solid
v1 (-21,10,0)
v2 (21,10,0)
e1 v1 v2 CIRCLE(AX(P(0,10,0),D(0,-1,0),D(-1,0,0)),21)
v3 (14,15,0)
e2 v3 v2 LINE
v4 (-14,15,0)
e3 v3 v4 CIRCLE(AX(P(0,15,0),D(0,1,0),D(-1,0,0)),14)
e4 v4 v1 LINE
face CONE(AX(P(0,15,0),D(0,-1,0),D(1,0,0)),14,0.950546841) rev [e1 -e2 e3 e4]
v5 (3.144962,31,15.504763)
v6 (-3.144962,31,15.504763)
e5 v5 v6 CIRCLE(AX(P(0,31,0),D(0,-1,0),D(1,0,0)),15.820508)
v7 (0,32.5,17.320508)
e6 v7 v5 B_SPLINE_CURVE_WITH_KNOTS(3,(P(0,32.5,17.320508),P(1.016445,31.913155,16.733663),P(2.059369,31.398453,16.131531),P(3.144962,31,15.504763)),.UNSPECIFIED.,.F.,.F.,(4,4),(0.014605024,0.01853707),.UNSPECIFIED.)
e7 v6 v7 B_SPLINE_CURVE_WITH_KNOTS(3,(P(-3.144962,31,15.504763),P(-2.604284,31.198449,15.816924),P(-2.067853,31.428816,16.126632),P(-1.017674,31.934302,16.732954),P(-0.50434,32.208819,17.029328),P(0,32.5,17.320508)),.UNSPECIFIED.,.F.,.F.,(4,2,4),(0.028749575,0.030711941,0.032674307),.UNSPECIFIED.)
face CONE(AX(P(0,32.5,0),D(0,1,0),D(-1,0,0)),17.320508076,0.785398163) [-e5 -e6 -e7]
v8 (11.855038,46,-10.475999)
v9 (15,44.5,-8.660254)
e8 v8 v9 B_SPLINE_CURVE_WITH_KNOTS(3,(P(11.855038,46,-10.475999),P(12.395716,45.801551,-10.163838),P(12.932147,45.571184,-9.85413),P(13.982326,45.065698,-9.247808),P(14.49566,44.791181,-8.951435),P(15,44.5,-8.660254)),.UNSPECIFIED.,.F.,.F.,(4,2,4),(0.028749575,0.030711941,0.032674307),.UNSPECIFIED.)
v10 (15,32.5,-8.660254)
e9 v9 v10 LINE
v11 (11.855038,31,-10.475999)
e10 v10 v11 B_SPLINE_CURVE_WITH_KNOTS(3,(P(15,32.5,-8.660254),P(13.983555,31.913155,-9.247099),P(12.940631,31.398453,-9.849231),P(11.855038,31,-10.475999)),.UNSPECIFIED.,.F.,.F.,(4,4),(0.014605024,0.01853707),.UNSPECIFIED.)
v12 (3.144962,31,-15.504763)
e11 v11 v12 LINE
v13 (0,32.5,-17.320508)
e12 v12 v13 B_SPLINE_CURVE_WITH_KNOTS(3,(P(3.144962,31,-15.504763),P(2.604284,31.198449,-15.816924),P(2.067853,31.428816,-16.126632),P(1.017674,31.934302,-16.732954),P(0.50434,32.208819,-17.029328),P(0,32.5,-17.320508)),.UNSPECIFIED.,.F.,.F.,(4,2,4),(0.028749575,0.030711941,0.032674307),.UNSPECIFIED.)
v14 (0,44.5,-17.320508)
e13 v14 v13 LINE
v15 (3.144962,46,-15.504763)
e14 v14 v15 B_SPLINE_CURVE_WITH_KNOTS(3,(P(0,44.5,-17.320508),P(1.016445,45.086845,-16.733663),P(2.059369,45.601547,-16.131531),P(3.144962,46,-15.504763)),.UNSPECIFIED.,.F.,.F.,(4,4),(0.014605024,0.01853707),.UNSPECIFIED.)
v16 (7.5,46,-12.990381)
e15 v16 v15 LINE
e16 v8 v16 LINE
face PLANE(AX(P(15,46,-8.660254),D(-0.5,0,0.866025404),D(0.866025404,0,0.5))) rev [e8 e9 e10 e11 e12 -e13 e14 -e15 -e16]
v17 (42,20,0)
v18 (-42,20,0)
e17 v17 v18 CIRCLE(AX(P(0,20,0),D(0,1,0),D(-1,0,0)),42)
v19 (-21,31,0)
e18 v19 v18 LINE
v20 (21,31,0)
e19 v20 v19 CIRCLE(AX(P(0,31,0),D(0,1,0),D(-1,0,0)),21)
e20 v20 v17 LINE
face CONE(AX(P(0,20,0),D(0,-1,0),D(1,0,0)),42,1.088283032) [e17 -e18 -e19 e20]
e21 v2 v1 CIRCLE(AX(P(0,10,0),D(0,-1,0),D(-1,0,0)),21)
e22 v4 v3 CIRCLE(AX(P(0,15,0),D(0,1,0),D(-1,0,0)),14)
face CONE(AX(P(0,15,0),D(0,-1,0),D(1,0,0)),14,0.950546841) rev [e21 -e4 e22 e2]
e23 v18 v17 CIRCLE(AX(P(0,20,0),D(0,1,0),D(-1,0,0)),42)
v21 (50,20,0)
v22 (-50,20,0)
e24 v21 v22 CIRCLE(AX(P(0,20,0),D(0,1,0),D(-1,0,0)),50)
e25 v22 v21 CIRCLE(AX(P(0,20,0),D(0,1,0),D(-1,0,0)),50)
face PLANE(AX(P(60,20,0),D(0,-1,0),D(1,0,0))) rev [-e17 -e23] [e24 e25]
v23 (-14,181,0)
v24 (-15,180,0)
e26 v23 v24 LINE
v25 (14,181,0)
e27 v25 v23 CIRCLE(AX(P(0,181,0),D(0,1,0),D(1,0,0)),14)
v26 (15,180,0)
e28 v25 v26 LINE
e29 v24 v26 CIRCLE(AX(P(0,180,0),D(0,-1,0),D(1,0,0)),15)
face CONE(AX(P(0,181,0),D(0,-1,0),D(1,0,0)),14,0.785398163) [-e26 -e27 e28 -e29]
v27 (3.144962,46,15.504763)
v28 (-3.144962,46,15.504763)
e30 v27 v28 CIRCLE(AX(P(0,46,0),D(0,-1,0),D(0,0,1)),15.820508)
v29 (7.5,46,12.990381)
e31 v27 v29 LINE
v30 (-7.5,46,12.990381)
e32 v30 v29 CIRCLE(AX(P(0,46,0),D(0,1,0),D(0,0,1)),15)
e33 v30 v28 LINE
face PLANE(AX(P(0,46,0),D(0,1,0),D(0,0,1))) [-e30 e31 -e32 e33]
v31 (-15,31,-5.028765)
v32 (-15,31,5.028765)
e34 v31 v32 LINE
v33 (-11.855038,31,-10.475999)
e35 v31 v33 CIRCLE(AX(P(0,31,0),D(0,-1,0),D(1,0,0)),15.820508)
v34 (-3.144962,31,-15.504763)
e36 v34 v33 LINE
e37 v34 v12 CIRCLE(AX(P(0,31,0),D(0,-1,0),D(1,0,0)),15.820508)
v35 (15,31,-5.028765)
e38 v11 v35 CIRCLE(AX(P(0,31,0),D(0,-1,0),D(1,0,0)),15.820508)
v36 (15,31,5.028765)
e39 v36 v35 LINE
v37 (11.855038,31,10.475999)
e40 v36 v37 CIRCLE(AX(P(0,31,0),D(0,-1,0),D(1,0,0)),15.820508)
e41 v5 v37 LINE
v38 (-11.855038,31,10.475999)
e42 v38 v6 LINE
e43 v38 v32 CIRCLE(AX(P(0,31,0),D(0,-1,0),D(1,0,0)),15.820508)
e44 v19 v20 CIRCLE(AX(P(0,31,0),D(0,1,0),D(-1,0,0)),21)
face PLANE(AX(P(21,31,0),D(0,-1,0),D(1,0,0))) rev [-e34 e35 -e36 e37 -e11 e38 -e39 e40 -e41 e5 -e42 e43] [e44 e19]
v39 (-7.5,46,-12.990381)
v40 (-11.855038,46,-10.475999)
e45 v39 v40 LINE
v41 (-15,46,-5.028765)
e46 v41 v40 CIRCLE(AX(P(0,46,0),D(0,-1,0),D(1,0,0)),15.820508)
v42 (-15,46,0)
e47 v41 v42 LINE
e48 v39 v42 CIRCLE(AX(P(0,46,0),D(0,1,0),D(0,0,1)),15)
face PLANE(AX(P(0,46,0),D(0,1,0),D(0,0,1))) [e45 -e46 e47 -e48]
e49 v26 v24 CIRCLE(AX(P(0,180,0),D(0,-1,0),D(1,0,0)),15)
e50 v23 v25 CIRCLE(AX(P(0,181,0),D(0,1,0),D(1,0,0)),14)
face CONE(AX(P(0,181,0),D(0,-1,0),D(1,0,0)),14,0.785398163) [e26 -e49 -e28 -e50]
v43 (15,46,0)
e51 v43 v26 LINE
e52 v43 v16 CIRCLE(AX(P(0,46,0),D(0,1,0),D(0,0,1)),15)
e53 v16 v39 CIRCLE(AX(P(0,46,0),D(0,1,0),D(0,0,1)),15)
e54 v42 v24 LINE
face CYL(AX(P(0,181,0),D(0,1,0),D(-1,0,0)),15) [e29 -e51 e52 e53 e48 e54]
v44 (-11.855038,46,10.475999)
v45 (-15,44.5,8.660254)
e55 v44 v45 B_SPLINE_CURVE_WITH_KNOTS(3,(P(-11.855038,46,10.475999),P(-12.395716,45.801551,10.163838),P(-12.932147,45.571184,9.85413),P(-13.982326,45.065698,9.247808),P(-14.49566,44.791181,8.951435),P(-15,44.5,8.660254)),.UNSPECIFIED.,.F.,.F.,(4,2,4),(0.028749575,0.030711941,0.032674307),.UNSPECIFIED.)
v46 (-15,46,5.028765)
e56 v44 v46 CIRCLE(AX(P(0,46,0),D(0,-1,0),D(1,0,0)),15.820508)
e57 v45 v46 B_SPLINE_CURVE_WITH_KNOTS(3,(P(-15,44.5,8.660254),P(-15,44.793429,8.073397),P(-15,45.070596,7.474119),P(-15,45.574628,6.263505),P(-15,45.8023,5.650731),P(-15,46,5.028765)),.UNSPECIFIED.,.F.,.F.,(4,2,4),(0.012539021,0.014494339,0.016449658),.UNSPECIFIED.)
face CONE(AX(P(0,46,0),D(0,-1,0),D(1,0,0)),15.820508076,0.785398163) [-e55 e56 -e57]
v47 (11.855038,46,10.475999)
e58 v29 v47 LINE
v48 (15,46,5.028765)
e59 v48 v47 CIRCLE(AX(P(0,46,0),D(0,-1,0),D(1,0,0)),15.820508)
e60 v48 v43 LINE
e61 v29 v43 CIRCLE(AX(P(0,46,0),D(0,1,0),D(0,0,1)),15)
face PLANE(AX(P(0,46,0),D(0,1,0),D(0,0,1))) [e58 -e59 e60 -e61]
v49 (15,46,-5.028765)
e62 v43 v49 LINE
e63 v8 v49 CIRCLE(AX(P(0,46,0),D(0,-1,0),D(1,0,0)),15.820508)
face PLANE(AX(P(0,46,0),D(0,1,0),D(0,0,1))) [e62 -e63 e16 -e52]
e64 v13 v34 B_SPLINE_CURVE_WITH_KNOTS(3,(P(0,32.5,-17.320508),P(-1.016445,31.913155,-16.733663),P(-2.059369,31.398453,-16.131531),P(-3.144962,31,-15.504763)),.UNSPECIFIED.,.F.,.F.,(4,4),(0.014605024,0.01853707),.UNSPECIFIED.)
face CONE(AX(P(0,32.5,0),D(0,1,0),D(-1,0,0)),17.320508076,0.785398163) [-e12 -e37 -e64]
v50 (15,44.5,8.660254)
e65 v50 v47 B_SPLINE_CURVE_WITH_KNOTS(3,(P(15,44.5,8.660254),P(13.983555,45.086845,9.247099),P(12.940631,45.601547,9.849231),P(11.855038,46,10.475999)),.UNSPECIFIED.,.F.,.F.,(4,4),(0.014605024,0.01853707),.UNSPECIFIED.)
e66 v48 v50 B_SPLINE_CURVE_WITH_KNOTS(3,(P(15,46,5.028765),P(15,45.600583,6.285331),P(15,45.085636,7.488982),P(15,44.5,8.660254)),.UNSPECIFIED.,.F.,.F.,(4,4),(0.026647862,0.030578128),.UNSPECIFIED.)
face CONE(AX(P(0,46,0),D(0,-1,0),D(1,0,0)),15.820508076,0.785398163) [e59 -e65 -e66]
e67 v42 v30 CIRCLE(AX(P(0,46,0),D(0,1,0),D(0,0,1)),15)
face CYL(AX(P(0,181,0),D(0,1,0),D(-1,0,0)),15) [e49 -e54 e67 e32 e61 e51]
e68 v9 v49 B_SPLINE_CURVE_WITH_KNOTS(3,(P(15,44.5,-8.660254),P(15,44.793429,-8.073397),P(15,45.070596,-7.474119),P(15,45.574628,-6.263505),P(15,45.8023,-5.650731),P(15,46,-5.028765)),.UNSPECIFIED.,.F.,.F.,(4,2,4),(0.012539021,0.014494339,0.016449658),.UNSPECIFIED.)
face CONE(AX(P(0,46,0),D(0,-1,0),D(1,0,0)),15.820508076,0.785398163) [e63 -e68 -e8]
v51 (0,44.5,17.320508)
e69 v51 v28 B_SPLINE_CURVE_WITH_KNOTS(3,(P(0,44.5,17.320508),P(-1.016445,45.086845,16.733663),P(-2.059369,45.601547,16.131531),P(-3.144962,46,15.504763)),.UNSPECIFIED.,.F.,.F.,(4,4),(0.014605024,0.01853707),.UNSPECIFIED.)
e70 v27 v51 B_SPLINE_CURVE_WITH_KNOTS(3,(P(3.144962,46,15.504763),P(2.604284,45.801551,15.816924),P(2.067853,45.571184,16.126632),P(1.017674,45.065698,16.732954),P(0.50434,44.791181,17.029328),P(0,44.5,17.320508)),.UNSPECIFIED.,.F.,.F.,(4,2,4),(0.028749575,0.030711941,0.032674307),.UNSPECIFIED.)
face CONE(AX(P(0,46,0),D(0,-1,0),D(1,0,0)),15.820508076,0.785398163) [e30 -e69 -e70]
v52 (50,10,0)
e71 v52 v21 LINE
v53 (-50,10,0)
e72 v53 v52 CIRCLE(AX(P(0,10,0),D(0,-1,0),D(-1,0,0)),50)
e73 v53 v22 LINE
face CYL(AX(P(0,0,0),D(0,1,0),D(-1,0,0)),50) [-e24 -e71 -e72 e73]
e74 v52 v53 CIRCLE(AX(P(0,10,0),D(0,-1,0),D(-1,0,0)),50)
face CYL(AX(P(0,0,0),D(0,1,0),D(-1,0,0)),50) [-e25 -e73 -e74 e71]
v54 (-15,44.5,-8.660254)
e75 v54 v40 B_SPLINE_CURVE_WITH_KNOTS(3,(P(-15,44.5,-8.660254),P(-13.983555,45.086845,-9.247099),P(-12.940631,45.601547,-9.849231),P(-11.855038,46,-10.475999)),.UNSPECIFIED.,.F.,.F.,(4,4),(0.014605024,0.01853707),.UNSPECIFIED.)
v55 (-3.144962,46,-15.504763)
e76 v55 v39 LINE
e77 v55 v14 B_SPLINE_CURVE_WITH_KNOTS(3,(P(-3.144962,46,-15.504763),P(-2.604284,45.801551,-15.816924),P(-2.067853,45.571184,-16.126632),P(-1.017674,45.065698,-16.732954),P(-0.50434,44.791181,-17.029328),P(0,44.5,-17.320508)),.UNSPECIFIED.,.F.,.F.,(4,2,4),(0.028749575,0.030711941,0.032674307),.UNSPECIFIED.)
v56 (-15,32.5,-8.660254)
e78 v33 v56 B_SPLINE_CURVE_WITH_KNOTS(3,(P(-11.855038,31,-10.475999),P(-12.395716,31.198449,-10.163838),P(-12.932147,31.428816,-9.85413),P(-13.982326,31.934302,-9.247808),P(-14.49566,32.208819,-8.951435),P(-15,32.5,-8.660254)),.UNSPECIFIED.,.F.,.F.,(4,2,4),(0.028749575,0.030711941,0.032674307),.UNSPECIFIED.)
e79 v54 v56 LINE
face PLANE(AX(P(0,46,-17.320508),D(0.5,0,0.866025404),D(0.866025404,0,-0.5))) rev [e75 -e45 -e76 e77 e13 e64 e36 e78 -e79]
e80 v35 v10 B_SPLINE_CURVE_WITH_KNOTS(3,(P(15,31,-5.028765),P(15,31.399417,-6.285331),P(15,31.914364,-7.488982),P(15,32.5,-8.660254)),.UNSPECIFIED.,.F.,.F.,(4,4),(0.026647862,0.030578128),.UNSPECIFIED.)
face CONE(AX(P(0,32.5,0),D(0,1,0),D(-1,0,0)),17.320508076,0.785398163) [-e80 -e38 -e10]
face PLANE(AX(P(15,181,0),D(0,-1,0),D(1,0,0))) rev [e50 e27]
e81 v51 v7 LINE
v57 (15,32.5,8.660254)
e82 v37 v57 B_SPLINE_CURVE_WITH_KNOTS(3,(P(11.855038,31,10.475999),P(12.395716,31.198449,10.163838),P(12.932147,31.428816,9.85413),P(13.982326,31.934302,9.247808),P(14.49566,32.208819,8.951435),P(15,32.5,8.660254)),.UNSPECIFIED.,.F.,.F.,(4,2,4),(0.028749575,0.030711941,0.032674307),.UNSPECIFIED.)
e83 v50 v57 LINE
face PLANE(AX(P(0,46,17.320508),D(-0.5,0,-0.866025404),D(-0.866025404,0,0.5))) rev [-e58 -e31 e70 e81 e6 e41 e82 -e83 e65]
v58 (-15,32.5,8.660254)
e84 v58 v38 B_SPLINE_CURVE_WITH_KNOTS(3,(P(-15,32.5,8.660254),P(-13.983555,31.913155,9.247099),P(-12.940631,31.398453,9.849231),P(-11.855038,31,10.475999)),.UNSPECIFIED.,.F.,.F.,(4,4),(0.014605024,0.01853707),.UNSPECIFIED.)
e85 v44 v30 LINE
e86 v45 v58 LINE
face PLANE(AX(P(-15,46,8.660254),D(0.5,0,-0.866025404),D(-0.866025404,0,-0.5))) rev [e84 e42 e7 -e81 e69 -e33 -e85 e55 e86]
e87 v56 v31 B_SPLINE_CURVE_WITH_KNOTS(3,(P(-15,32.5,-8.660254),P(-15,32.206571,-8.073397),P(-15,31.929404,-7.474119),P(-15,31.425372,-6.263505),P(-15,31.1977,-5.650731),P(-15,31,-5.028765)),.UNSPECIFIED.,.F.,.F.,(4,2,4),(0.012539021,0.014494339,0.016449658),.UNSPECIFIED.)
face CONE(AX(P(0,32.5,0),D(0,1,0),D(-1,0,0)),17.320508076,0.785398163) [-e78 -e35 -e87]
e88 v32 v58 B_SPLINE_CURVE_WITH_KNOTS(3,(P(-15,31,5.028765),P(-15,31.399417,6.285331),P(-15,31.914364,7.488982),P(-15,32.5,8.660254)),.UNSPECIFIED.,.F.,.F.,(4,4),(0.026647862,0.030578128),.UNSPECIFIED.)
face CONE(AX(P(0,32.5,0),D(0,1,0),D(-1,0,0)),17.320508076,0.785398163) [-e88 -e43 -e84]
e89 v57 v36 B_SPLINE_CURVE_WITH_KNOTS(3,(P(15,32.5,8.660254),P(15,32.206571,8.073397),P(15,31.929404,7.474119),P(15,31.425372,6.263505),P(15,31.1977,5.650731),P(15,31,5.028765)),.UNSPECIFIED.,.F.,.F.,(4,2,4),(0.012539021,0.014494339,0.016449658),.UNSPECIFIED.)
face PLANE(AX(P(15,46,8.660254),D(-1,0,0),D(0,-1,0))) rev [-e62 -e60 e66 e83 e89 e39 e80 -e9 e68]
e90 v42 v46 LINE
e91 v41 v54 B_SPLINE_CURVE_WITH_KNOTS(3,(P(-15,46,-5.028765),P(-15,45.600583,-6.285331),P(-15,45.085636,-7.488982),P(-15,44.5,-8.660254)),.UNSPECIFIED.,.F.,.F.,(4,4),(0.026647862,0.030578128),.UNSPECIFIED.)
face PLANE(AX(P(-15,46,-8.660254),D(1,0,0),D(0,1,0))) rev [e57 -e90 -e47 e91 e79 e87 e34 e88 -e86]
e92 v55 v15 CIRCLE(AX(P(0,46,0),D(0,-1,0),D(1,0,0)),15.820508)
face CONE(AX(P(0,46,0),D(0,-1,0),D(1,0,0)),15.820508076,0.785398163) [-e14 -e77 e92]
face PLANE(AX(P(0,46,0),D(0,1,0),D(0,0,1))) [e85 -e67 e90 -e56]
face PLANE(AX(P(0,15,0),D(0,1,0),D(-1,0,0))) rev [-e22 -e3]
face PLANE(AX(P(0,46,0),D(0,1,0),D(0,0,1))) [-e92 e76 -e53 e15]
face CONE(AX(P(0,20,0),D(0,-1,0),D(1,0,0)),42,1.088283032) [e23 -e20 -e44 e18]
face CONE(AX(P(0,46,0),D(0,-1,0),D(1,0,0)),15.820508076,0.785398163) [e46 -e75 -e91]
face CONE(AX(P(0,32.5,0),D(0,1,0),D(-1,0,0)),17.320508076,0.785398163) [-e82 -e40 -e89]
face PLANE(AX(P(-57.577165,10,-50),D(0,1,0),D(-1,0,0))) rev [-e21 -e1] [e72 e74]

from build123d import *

# Parameters (mm, degrees)
BOSS_EXTRUDE1_DEPTH     = 15
CHAMFER1_SIZE           = 1
SKETCH4_R               = 79.861717746
SKETCH4_R_2             = 50
CUT_EXTRUDE1_DEPTH      = 182.991758055
CUT_EXTRUDE2_DEPTH      = 195.321897891
CUT_EXTRUDE2_DEPTH_BACK = 195.321897891
SKETCH5_W               = 151.709550381
SKETCH5_H               = 33.031628388


with BuildPart() as part:
    # Sketch1 → Revolve1 (revolve)
    with BuildSketch(Plane.XY, mode=Mode.PRIVATE) as revolve1_sk:
        Polygon((35, 0), (60, 0), (60, 9.5), (59.5, 10), (60, 10.5), (60, 20), (42, 20), (21, 31), (15, 31), (15, 181), (0, 181), (0, 15), (14, 15), align=None)
    revolve(revolve1_sk.sketch.rotate(Axis((0, 181, 0), (0, -1, 0)), 180), axis=Axis((0, 181, 0), (0, -1, 0)))

    # Sketch2 → Boss-Extrude1 (add)
    with BuildSketch(Plane(origin=(0, 31, 0), x_dir=(1, 0, 0), z_dir=(0, 1, 0))):
        Polygon((15, 8.660254038), (0, 17.320508076), (-15, 8.660254038), (-15, -8.660254038), (0, -17.320508076), (15, -8.660254038), align=None)
    extrude(amount=BOSS_EXTRUDE1_DEPTH)

    # Sketch3 → Cut-Revolve1 (revolve, cut)
    with BuildSketch(Plane(origin=(0, 0, 0), x_dir=(0, 0, -1), z_dir=(1, 0, 0))):
        Polygon((15.820508076, 31), (17.320508076, 32.5), (17.320508076, 31), align=None)
        Polygon((17.320508076, 44.5), (15.820508076, 46), (17.320508076, 46), align=None)
    revolve(axis=Axis((0, 181, 0), (0, 1, 0)), mode=Mode.SUBTRACT)

    # Chamfer1
    chamfer1_edges = [part.edges().sort_by_distance(p)[0] for p in [
        (15, 181, 0),
    ]]
    chamfer(chamfer1_edges, length=CHAMFER1_SIZE)

    # Sketch4 → Cut-Extrude1 (cut, through all)
    with BuildSketch(Plane(origin=(0, 20, 0), x_dir=(1, 0, 0), z_dir=(0, 1, 0))):
        Circle(SKETCH4_R)
        with Locations(Location((0, 0, 0), (0, 0, 180))):
            Circle(SKETCH4_R_2, mode=Mode.SUBTRACT)
    extrude(amount=-CUT_EXTRUDE1_DEPTH, mode=Mode.SUBTRACT)

    # Sketch5 → Cut-Extrude2 (cut, two sides: drawn at the far end of the back side and taken through both)
    with BuildSketch(Plane.XY.offset(-CUT_EXTRUDE2_DEPTH_BACK)):
        with Locations((18.277609901, -6.515814194)):
            Rectangle(SKETCH5_W, SKETCH5_H)
    extrude(amount=CUT_EXTRUDE2_DEPTH + CUT_EXTRUDE2_DEPTH_BACK, mode=Mode.SUBTRACT)


solid = part.part
